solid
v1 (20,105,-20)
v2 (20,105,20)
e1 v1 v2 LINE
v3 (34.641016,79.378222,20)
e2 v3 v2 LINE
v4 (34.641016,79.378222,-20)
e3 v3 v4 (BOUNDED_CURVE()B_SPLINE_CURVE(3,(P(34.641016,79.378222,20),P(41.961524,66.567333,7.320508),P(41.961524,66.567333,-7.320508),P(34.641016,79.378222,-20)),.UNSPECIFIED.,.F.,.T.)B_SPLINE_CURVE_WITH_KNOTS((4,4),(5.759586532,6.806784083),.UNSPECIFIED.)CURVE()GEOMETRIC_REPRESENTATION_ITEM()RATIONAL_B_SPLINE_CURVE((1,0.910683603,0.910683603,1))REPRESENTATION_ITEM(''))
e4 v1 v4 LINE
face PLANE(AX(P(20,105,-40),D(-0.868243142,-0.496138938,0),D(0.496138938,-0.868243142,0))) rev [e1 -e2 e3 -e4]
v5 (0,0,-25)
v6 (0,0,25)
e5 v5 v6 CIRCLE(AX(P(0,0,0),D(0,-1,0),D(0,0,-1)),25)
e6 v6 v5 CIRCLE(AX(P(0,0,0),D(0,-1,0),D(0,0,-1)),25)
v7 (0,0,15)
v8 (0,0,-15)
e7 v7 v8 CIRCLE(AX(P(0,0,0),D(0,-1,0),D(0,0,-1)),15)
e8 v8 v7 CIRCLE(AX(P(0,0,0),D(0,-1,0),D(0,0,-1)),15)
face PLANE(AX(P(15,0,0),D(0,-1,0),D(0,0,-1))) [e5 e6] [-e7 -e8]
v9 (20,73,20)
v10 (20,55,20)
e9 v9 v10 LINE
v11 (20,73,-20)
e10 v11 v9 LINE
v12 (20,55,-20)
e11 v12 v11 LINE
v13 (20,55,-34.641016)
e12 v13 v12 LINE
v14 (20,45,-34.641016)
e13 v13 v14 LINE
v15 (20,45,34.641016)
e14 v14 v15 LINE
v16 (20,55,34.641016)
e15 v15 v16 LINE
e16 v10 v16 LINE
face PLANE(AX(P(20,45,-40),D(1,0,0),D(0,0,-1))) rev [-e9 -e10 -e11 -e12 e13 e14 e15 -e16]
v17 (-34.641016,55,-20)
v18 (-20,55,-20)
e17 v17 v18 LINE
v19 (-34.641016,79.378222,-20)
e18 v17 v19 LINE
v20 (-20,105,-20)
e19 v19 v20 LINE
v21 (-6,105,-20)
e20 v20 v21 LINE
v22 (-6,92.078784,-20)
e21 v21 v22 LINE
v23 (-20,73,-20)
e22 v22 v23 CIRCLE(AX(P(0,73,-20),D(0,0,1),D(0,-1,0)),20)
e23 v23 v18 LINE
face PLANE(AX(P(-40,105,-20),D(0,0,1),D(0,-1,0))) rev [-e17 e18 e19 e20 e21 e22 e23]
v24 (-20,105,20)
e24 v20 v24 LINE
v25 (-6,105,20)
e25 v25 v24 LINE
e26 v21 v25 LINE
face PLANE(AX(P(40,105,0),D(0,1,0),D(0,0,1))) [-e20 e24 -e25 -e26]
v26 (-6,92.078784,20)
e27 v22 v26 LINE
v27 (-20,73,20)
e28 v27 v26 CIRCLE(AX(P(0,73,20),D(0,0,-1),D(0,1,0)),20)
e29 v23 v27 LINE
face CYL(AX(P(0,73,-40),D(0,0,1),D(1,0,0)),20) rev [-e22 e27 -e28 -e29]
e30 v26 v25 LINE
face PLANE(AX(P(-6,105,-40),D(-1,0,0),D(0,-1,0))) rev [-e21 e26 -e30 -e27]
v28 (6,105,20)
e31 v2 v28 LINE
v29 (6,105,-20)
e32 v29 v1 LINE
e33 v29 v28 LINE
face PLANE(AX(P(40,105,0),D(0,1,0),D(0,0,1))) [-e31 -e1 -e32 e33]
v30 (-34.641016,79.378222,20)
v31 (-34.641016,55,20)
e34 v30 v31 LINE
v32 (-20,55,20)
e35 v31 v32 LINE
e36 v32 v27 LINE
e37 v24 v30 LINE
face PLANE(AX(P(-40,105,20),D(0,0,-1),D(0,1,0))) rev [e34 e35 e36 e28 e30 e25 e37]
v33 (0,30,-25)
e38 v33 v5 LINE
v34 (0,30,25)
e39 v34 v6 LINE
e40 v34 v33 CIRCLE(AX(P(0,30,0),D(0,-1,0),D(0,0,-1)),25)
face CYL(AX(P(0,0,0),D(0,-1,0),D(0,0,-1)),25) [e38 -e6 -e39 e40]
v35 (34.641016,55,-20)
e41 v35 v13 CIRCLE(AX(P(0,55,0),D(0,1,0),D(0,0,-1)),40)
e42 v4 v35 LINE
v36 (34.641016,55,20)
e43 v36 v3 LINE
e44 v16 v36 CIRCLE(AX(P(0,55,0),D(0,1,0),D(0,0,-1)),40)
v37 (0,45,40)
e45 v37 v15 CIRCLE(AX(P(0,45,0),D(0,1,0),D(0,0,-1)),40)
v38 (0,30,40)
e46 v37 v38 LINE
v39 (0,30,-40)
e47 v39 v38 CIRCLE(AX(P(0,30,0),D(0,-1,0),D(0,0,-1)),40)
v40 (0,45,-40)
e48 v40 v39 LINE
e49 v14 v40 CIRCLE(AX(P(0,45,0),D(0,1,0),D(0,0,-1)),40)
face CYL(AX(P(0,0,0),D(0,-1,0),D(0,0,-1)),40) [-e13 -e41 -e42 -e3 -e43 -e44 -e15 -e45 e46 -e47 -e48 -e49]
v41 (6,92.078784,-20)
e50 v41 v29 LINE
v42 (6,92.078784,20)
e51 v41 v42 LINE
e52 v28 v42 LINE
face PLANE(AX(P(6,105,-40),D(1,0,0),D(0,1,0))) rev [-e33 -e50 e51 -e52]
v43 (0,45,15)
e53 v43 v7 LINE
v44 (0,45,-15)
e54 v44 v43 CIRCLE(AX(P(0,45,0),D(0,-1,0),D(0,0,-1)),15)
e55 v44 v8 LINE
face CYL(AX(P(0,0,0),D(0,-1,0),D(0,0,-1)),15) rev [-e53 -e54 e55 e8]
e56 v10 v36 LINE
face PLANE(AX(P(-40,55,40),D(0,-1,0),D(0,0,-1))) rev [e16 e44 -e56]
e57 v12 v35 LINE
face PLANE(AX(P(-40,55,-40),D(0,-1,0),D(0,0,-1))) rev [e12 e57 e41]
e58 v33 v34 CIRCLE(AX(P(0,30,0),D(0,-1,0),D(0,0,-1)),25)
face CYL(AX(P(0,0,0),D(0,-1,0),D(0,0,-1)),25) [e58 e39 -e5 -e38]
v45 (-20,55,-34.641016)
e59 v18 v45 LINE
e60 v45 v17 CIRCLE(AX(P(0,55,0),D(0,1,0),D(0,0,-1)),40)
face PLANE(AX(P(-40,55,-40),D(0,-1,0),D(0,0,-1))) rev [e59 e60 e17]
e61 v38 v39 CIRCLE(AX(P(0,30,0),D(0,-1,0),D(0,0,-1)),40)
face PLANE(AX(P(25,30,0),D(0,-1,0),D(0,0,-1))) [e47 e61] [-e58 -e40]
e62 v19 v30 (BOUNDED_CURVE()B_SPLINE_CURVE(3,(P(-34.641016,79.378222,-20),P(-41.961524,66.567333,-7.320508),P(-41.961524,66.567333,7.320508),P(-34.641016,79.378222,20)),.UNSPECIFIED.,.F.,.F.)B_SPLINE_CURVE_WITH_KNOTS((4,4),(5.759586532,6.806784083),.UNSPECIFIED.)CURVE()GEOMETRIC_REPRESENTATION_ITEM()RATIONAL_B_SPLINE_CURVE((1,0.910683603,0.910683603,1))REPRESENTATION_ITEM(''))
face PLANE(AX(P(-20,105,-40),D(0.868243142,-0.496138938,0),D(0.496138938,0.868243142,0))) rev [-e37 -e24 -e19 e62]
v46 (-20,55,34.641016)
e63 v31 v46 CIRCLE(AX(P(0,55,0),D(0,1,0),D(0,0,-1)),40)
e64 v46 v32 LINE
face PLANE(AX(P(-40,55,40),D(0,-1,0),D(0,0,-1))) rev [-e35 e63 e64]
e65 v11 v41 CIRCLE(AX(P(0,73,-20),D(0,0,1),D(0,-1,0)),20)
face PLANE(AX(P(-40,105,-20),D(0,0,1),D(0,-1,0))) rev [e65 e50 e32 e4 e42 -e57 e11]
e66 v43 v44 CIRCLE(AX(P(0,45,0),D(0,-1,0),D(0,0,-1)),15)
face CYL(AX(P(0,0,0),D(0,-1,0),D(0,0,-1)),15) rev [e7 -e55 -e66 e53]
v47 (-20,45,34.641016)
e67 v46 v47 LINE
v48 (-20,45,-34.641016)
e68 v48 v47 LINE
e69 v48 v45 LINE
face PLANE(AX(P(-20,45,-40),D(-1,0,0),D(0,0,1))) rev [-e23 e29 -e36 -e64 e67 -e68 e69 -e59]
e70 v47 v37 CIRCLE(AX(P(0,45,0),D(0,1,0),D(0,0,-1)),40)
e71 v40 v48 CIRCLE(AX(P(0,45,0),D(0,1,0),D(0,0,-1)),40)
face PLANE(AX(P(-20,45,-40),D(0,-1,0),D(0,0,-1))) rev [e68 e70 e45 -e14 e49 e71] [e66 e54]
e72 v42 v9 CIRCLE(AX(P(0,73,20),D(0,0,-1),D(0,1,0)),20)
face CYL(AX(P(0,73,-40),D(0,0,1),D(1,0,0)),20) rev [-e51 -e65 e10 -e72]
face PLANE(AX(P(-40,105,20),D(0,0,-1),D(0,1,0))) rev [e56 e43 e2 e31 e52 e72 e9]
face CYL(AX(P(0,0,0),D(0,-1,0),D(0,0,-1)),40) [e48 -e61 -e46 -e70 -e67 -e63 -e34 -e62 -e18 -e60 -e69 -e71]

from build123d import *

# Parameters (mm, degrees)
FORK_SIDE_PROFILE_CUT_DEPTH      = 120.268604419
FORK_SIDE_PROFILE_CUT_DEPTH_BACK = 120.268604419
FORK_SIDE_PROFILE_SKETCH_W       = 20
FORK_SIDE_PROFILE_SKETCH_H       = 50
FORK_SLOT_CUT_DEPTH              = 120.268604419
FORK_SLOT_CUT_DEPTH_BACK         = 120.268604419


with BuildPart() as part:
    # Body Profile Sketch → Revolved Body (revolve)
    with BuildSketch(Plane.XY, mode=Mode.PRIVATE) as revolved_body_sk:
        Polygon((15, 0), (25, 0), (25, 30), (40, 30), (40, 105), (0, 105), (0, 55), (15, 55), align=None)
    revolve(revolved_body_sk.sketch.rotate(Axis((0, 0, 0), (0, 1, 0)), 90), axis=Axis((0, 0, 0), (0, 1, 0)))

    # Fork Side Profile Sketch → Fork Side Profile Cut (cut, two sides: drawn at the far end of the back side and taken through both)
    with BuildSketch(Plane(origin=(0, 0, 0), x_dir=(0, 0, -1), z_dir=(1, 0, 0)).offset(-FORK_SIDE_PROFILE_CUT_DEPTH_BACK)):
        with Locations((-30, 80)):
            Rectangle(FORK_SIDE_PROFILE_SKETCH_W, FORK_SIDE_PROFILE_SKETCH_H)
        with Locations((30, 80)):
            Rectangle(FORK_SIDE_PROFILE_SKETCH_W, FORK_SIDE_PROFILE_SKETCH_H)
    extrude(amount=FORK_SIDE_PROFILE_CUT_DEPTH + FORK_SIDE_PROFILE_CUT_DEPTH_BACK, mode=Mode.SUBTRACT)

    # Fork Slot Sketch → Fork Slot Cut (cut, two sides: drawn at the far end of the back side and taken through both)
    with BuildSketch(Plane.XY.offset(-FORK_SLOT_CUT_DEPTH_BACK)):
        Polygon((-40, 105), (-20, 105), (-40, 70), align=None)
        Polygon((40, 105), (20, 105), (40, 70), align=None)
        with BuildLine():
            Line((-20, 45), (20, 45))
            Line((20, 45), (20, 73))
            ThreePointArc((20, 73), (16.124515497, 84.832159566), (6, 92.078784028))
            Line((6, 92.078784028), (6, 105))
            Line((6, 105), (-6, 105))
            Line((-6, 105), (-6, 92.078784028))
            ThreePointArc((-6, 92.078784028), (-16.124515497, 84.832159566), (-20, 73))
            Line((-20, 73), (-20, 45))
        make_face()
    extrude(amount=FORK_SLOT_CUT_DEPTH + FORK_SLOT_CUT_DEPTH_BACK, mode=Mode.SUBTRACT)


solid = part.part
